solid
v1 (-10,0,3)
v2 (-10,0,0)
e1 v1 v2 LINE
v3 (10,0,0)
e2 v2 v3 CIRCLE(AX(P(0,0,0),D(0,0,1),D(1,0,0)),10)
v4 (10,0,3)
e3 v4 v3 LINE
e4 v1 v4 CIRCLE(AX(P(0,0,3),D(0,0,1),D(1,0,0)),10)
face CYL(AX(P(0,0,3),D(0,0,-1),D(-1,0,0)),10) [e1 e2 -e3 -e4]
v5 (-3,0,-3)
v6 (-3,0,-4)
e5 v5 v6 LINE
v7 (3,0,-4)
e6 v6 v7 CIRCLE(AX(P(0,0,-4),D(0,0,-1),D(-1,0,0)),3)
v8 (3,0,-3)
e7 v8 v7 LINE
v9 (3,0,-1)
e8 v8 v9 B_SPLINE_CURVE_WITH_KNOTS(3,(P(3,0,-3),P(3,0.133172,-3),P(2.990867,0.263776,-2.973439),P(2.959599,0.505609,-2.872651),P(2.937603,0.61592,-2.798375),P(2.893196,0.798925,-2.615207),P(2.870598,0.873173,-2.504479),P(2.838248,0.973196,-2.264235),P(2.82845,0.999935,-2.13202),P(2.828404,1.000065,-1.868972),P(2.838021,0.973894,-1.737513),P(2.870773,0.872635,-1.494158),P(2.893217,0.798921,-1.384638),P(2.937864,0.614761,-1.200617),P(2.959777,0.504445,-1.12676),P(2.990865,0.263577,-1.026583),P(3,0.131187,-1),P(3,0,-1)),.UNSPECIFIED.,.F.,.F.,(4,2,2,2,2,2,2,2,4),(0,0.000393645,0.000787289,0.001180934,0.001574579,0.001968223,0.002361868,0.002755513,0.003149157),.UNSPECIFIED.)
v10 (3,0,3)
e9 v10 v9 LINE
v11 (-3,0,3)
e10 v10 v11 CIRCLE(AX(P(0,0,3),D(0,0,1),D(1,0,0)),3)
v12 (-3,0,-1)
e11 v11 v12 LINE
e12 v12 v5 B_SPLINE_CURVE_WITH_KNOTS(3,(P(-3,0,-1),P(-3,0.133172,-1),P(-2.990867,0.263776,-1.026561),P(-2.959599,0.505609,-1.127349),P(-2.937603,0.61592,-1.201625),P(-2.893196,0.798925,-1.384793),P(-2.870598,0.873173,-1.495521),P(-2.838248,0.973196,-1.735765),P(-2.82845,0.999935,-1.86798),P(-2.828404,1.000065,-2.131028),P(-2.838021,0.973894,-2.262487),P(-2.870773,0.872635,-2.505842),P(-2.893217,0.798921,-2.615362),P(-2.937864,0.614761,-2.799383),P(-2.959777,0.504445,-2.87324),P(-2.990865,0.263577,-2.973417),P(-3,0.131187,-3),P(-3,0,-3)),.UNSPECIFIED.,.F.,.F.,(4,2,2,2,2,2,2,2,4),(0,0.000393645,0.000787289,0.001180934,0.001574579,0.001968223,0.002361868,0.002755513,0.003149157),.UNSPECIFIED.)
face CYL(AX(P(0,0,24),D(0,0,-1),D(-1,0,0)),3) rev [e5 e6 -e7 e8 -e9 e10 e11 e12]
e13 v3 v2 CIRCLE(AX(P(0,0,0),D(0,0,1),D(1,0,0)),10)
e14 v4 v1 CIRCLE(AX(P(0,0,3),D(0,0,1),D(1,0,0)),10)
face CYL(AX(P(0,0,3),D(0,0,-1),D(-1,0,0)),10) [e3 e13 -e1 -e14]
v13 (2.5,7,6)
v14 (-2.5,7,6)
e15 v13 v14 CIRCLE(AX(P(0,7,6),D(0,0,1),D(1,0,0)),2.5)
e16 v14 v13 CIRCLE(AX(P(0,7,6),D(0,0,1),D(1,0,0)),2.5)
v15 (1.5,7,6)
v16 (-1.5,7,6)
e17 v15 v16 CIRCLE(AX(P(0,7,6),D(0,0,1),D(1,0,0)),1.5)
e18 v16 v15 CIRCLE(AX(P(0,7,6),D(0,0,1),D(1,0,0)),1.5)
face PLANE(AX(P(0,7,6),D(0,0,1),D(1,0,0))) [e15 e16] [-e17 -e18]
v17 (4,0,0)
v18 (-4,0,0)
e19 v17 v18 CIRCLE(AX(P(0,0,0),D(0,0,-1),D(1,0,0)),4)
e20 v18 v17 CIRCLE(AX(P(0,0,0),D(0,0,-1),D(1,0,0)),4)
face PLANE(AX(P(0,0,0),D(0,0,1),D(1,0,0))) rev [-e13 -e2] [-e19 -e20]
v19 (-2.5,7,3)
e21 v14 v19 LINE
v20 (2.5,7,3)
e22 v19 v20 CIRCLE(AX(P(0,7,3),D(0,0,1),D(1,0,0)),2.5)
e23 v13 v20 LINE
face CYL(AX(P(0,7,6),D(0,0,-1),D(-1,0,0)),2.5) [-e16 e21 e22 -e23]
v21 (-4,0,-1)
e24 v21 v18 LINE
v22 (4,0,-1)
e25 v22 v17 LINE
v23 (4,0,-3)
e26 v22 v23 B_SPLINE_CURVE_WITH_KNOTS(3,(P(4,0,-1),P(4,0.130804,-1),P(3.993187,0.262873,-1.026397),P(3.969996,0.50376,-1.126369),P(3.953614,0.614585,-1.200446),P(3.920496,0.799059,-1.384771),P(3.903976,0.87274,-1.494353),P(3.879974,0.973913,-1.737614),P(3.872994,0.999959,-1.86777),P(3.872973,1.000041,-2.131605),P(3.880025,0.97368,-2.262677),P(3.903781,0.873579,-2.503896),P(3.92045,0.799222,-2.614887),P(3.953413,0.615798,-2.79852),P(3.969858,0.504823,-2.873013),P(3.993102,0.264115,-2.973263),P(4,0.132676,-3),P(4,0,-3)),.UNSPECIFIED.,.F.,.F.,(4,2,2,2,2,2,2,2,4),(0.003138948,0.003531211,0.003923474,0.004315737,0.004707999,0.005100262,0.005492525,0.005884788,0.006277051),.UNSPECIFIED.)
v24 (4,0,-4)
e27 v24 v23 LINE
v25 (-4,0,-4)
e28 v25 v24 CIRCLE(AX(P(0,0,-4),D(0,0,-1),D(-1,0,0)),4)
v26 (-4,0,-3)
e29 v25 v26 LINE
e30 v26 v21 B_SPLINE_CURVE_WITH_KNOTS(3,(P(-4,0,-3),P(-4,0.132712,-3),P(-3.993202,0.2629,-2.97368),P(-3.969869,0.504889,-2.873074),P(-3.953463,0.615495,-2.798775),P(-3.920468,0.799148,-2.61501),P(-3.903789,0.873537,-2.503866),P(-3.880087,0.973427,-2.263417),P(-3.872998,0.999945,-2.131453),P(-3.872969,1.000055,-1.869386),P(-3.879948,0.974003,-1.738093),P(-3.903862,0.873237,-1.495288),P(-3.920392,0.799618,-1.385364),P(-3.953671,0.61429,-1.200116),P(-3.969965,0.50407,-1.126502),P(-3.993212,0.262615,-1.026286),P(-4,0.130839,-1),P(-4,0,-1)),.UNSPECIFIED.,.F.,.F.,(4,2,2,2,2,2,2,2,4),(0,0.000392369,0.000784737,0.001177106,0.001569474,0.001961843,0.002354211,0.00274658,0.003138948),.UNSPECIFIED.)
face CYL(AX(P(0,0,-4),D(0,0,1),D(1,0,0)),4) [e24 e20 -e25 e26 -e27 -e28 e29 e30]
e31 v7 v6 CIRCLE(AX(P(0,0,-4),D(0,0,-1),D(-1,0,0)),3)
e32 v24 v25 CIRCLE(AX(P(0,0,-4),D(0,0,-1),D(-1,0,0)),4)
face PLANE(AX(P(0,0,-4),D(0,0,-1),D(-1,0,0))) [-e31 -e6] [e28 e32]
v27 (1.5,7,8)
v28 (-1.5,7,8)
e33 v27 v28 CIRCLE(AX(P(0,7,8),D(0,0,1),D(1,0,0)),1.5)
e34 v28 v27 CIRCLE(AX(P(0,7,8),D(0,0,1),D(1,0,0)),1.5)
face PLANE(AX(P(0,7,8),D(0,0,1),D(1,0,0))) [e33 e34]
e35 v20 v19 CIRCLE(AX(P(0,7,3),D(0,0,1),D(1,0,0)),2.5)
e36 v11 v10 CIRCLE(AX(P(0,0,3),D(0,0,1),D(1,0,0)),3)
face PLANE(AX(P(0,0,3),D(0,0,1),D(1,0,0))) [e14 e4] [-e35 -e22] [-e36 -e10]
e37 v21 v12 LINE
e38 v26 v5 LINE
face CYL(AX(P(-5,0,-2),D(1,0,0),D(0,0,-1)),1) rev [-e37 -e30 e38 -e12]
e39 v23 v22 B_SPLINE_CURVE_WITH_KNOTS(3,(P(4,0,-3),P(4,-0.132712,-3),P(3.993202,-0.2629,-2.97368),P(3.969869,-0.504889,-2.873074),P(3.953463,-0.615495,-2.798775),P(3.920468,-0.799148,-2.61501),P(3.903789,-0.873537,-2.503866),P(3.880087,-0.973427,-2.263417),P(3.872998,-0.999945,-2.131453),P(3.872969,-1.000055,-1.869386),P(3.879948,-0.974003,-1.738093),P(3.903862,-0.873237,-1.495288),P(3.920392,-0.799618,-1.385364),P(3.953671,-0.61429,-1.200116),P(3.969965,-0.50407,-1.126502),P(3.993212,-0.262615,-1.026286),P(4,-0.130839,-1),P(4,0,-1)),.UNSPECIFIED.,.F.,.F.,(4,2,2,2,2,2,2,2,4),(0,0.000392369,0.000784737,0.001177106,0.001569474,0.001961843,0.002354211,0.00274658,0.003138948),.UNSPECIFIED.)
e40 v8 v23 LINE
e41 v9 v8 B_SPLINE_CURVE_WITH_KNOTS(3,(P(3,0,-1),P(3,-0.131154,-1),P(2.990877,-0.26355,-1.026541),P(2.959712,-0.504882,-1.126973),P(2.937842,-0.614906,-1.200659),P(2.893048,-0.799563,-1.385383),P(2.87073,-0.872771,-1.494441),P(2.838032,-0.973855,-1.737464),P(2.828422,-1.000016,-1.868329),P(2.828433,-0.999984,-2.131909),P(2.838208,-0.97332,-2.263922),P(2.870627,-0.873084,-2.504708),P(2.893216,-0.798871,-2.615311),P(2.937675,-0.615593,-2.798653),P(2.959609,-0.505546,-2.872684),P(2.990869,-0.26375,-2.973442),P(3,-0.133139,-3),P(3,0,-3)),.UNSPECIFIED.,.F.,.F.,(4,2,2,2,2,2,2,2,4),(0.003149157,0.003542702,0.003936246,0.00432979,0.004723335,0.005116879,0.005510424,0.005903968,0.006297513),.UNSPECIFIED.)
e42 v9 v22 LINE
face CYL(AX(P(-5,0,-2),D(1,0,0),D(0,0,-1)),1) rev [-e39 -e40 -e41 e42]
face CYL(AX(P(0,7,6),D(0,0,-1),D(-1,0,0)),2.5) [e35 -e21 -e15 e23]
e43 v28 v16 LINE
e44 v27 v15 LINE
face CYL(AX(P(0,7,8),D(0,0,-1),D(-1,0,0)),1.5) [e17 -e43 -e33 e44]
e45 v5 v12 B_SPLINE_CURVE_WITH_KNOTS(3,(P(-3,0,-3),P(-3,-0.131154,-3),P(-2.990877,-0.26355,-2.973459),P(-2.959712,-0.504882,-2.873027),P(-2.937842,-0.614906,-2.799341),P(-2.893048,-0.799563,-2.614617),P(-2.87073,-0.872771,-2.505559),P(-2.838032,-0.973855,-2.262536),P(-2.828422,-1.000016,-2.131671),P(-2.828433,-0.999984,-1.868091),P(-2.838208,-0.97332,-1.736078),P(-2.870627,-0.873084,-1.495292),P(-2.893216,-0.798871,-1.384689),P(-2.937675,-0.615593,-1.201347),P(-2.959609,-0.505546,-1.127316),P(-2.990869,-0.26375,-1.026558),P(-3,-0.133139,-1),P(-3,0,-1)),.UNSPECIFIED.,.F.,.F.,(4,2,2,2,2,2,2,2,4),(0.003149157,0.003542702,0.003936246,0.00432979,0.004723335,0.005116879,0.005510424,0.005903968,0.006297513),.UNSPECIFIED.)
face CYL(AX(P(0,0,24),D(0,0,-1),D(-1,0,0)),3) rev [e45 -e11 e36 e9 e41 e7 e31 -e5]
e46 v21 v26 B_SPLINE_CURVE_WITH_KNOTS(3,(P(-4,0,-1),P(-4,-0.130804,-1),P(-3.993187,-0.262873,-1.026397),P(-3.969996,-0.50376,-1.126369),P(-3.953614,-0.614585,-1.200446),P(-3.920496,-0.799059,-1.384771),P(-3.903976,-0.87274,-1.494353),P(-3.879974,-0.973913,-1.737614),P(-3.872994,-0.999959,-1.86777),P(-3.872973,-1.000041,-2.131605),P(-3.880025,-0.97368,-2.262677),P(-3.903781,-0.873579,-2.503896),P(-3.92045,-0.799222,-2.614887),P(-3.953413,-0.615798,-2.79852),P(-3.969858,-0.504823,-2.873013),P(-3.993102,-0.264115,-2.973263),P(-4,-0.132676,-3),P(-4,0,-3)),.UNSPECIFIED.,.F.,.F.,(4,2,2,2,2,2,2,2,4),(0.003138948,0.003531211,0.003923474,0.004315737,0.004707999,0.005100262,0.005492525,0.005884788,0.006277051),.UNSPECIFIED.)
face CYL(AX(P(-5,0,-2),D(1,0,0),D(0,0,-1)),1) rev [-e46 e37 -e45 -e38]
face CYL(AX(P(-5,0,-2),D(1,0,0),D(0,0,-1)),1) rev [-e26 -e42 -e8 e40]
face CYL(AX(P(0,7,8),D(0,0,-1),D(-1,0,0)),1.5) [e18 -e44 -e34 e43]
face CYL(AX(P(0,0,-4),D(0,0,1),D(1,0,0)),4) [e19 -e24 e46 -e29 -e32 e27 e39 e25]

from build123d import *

# Parameters (mm, degrees)
SKETCH1_R           = 10
BOSS_EXTRUDE1_DEPTH = 3
SKETCH2_R           = 2.5
BOSS_EXTRUDE2_DEPTH = 3
SKETCH3_R           = 1.5
BOSS_EXTRUDE3_DEPTH = 2
SKETCH4_R           = 3
CUT_EXTRUDE1_DEPTH  = 24
BOSS_EXTRUDE4_START = 4
SKETCH5_R           = 4
SKETCH5_R_2         = 3
BOSS_EXTRUDE4_DEPTH = 4
SKETCH6_R           = 1
CUT_EXTRUDE2_DEPTH  = 5


with BuildPart() as part:
    # Sketch1 → Boss-Extrude1 (new body)
    with BuildSketch(Plane.XY):
        Circle(SKETCH1_R)
    extrude(amount=BOSS_EXTRUDE1_DEPTH)

    # Sketch2 → Boss-Extrude2 (add)
    with BuildSketch(Plane.XY.offset(3)):
        with Locations((0, 7)):
            Circle(SKETCH2_R)
    extrude(amount=BOSS_EXTRUDE2_DEPTH)

    # Sketch3 → Boss-Extrude3 (add)
    with BuildSketch(Plane.XY.offset(6)):
        with Locations((0, 7)):
            Circle(SKETCH3_R)
    extrude(amount=BOSS_EXTRUDE3_DEPTH)

    # Sketch4 → Cut-Extrude1 (cut)
    with BuildSketch(Plane(origin=(0, 0, 0), x_dir=(-1, 0, 0), z_dir=(0, 0, -1))):
        Circle(SKETCH4_R)
    extrude(amount=-CUT_EXTRUDE1_DEPTH, mode=Mode.SUBTRACT)

    # Sketch5 → Boss-Extrude4 (add)
    with BuildSketch(Plane(origin=(0, 0, 0), x_dir=(-1, 0, 0), z_dir=(0, 0, -1)).offset(BOSS_EXTRUDE4_START)):
        with Locations(Location((0, 0, 0), (0, 0, 180))):
            Circle(SKETCH5_R)
        Circle(SKETCH5_R_2, mode=Mode.SUBTRACT)
    extrude(amount=-BOSS_EXTRUDE4_DEPTH)

    # Sketch6 → Cut-Extrude2 (cut, symmetric)
    with BuildSketch(Plane(origin=(0, 0, 0), x_dir=(0, 0, -1), z_dir=(1, 0, 0))):
        with Locations((2, 0)):
            Circle(SKETCH6_R)
    extrude(amount=CUT_EXTRUDE2_DEPTH, both=True, mode=Mode.SUBTRACT)


solid = part.part
